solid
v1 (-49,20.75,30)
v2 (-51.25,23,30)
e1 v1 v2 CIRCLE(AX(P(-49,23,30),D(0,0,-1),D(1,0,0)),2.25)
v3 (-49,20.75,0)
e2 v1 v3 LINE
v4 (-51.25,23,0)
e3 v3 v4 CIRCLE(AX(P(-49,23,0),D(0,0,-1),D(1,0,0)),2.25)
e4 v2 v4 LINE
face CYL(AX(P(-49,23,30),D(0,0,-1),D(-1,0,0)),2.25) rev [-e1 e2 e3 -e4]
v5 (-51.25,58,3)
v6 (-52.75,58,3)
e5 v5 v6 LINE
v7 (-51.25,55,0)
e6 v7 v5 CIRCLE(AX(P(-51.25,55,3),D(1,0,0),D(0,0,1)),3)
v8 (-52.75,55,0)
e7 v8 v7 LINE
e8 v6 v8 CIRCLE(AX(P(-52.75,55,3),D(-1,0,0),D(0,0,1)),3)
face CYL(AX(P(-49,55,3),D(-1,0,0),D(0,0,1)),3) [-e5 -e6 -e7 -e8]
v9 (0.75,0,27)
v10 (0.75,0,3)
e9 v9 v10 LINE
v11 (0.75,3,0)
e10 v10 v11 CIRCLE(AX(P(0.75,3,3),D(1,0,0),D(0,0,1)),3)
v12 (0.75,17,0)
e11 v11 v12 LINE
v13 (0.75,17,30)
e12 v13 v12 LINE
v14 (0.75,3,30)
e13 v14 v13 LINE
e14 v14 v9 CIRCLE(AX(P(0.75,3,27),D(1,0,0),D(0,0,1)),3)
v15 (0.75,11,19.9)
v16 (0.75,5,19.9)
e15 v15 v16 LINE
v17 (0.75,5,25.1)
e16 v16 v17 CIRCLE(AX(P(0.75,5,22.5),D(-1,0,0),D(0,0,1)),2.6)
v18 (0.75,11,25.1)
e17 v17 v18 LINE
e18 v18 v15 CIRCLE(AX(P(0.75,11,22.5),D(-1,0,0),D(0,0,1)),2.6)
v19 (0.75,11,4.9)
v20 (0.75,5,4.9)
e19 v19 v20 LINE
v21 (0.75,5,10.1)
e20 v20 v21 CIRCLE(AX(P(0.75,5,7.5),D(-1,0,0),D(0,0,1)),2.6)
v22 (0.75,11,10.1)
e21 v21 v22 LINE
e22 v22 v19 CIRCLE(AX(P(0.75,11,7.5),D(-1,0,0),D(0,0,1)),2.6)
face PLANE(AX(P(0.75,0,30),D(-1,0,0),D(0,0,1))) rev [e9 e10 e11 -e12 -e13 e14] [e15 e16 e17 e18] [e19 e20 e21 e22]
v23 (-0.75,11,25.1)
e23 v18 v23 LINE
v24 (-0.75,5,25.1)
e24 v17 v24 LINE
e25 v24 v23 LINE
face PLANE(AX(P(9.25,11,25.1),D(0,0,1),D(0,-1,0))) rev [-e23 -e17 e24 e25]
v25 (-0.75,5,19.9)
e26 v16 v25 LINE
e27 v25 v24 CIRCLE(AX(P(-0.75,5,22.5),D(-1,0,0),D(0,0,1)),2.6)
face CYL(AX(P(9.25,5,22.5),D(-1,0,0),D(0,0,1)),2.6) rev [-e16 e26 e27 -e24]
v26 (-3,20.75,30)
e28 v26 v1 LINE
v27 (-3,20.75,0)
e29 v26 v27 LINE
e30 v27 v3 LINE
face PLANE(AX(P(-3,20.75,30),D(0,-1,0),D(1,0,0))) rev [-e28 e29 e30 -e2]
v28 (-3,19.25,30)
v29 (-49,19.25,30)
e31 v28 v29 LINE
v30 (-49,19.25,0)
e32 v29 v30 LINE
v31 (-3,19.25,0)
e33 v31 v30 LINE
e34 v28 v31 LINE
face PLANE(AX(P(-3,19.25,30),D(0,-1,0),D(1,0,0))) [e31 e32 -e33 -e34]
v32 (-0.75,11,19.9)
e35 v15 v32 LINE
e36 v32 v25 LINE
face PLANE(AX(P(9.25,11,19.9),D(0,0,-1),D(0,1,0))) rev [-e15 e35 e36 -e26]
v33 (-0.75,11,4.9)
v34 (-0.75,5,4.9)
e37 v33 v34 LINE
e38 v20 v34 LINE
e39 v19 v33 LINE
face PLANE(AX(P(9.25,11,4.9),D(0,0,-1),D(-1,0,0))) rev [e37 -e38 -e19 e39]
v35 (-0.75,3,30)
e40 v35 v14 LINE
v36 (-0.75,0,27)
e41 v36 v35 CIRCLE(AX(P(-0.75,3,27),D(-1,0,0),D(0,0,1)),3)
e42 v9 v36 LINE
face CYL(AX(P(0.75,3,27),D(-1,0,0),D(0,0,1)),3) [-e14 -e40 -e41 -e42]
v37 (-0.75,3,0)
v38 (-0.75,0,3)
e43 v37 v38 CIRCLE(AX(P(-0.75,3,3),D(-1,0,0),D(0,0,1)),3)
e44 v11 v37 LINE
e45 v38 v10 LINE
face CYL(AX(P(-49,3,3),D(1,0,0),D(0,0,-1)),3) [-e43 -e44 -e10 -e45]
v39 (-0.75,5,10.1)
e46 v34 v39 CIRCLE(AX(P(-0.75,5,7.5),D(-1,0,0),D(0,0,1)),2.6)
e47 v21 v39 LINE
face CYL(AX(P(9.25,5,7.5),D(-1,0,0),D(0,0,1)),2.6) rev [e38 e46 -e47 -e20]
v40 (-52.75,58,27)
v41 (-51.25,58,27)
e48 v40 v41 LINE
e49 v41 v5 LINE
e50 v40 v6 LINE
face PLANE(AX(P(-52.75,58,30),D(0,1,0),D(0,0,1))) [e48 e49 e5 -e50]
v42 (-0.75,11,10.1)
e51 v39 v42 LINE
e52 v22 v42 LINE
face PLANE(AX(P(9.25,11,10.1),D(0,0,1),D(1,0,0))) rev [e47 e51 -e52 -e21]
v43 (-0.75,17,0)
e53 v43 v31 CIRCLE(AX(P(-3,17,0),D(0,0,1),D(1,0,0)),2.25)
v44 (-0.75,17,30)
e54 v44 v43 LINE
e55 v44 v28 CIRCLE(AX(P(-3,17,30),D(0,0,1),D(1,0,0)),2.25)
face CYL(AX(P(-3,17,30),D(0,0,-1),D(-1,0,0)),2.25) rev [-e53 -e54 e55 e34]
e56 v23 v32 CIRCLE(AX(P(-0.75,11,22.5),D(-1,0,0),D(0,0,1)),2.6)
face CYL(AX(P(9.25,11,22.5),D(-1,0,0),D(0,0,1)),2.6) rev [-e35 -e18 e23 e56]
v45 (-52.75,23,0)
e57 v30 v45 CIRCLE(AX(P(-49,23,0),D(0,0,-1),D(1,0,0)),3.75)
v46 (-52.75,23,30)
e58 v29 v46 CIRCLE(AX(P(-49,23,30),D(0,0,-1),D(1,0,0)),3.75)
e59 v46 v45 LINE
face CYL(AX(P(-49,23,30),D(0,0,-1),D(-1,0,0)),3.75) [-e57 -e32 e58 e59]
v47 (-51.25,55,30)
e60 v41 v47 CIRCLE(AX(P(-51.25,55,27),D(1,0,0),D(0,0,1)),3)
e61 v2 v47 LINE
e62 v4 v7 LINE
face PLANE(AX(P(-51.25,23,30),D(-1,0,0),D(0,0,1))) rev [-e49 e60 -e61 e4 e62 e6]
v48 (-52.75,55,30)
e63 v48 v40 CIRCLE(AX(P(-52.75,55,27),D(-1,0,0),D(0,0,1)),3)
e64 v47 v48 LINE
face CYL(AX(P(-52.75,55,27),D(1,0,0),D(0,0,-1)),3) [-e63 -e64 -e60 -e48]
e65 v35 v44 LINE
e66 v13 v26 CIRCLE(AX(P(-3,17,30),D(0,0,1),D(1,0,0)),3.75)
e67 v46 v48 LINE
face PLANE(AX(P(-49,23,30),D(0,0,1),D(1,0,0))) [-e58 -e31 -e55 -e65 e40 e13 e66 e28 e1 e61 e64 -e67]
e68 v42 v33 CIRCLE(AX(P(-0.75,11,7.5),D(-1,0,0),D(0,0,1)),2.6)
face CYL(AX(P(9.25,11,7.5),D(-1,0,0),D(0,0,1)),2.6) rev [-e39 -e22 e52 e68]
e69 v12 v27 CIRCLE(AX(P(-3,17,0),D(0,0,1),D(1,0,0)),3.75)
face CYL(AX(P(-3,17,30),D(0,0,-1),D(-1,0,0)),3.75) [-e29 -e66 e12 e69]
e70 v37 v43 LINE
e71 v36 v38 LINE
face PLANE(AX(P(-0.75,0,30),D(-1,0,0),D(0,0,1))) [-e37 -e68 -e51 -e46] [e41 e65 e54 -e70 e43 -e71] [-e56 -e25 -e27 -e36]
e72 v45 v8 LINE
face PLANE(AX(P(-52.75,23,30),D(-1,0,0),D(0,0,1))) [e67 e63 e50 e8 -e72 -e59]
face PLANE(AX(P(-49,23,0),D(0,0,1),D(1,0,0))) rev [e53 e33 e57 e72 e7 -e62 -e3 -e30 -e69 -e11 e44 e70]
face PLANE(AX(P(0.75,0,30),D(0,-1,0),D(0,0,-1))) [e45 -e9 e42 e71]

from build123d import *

# Parameters (mm, degrees)
EXTRUDE_1_DEPTH     = 30
FILLET_1_R          = 3
CUT_EXTRUDE_1_DEPTH = 10


with BuildPart() as part:
    # 草图1 → 拉伸-薄壁1 (new body)
    with BuildSketch(Plane.XY):
        with BuildLine():
            Line((0.75, 0), (0.75, 17))
            ThreePointArc((0.75, 17), (-0.348349571, 19.651650429), (-3, 20.75))
            Line((-3, 20.75), (-49, 20.75))
            ThreePointArc((-49, 20.75), (-50.590990258, 21.409009742), (-51.25, 23))
            Line((-51.25, 23), (-51.25, 58))
            Line((-51.25, 58), (-52.75, 58))
            Line((-52.75, 58), (-52.75, 23))
            ThreePointArc((-52.75, 23), (-51.651650429, 20.348349571), (-49, 19.25))
            Line((-49, 19.25), (-3, 19.25))
            ThreePointArc((-3, 19.25), (-1.409009742, 18.590990258), (-0.75, 17))
            Line((-0.75, 17), (-0.75, 0))
            Line((-0.75, 0), (0.75, 0))
        make_face()
    extrude(amount=EXTRUDE_1_DEPTH)

    # 圆角1
    fillet_1_edges = [part.edges().sort_by_distance(p)[0] for p in [
        (0, 0, 0),
        (-52, 58, 0),
        (0, 0, 30),
        (-52, 58, 30),
    ]]
    fillet(fillet_1_edges, radius=FILLET_1_R)

    # 草图2 → 切除-拉伸1 (cut)
    with BuildSketch(Plane.ZY.offset(0.75)):
        with BuildLine():
            Line((10.1, 11), (10.1, 5))
            ThreePointArc((10.1, 5), (7.5, 2.4), (4.9, 5))
            Line((4.9, 5), (4.9, 11))
            ThreePointArc((4.9, 11), (7.5, 13.6), (10.1, 11))
        make_face()
        with BuildLine():
            Line((25.1, 11), (25.1, 5))
            ThreePointArc((25.1, 5), (22.5, 2.4), (19.9, 5))
            Line((19.9, 5), (19.9, 11))
            ThreePointArc((19.9, 11), (22.5, 13.6), (25.1, 11))
        make_face()
    extrude(amount=-CUT_EXTRUDE_1_DEPTH, mode=Mode.SUBTRACT)


solid = part.part
